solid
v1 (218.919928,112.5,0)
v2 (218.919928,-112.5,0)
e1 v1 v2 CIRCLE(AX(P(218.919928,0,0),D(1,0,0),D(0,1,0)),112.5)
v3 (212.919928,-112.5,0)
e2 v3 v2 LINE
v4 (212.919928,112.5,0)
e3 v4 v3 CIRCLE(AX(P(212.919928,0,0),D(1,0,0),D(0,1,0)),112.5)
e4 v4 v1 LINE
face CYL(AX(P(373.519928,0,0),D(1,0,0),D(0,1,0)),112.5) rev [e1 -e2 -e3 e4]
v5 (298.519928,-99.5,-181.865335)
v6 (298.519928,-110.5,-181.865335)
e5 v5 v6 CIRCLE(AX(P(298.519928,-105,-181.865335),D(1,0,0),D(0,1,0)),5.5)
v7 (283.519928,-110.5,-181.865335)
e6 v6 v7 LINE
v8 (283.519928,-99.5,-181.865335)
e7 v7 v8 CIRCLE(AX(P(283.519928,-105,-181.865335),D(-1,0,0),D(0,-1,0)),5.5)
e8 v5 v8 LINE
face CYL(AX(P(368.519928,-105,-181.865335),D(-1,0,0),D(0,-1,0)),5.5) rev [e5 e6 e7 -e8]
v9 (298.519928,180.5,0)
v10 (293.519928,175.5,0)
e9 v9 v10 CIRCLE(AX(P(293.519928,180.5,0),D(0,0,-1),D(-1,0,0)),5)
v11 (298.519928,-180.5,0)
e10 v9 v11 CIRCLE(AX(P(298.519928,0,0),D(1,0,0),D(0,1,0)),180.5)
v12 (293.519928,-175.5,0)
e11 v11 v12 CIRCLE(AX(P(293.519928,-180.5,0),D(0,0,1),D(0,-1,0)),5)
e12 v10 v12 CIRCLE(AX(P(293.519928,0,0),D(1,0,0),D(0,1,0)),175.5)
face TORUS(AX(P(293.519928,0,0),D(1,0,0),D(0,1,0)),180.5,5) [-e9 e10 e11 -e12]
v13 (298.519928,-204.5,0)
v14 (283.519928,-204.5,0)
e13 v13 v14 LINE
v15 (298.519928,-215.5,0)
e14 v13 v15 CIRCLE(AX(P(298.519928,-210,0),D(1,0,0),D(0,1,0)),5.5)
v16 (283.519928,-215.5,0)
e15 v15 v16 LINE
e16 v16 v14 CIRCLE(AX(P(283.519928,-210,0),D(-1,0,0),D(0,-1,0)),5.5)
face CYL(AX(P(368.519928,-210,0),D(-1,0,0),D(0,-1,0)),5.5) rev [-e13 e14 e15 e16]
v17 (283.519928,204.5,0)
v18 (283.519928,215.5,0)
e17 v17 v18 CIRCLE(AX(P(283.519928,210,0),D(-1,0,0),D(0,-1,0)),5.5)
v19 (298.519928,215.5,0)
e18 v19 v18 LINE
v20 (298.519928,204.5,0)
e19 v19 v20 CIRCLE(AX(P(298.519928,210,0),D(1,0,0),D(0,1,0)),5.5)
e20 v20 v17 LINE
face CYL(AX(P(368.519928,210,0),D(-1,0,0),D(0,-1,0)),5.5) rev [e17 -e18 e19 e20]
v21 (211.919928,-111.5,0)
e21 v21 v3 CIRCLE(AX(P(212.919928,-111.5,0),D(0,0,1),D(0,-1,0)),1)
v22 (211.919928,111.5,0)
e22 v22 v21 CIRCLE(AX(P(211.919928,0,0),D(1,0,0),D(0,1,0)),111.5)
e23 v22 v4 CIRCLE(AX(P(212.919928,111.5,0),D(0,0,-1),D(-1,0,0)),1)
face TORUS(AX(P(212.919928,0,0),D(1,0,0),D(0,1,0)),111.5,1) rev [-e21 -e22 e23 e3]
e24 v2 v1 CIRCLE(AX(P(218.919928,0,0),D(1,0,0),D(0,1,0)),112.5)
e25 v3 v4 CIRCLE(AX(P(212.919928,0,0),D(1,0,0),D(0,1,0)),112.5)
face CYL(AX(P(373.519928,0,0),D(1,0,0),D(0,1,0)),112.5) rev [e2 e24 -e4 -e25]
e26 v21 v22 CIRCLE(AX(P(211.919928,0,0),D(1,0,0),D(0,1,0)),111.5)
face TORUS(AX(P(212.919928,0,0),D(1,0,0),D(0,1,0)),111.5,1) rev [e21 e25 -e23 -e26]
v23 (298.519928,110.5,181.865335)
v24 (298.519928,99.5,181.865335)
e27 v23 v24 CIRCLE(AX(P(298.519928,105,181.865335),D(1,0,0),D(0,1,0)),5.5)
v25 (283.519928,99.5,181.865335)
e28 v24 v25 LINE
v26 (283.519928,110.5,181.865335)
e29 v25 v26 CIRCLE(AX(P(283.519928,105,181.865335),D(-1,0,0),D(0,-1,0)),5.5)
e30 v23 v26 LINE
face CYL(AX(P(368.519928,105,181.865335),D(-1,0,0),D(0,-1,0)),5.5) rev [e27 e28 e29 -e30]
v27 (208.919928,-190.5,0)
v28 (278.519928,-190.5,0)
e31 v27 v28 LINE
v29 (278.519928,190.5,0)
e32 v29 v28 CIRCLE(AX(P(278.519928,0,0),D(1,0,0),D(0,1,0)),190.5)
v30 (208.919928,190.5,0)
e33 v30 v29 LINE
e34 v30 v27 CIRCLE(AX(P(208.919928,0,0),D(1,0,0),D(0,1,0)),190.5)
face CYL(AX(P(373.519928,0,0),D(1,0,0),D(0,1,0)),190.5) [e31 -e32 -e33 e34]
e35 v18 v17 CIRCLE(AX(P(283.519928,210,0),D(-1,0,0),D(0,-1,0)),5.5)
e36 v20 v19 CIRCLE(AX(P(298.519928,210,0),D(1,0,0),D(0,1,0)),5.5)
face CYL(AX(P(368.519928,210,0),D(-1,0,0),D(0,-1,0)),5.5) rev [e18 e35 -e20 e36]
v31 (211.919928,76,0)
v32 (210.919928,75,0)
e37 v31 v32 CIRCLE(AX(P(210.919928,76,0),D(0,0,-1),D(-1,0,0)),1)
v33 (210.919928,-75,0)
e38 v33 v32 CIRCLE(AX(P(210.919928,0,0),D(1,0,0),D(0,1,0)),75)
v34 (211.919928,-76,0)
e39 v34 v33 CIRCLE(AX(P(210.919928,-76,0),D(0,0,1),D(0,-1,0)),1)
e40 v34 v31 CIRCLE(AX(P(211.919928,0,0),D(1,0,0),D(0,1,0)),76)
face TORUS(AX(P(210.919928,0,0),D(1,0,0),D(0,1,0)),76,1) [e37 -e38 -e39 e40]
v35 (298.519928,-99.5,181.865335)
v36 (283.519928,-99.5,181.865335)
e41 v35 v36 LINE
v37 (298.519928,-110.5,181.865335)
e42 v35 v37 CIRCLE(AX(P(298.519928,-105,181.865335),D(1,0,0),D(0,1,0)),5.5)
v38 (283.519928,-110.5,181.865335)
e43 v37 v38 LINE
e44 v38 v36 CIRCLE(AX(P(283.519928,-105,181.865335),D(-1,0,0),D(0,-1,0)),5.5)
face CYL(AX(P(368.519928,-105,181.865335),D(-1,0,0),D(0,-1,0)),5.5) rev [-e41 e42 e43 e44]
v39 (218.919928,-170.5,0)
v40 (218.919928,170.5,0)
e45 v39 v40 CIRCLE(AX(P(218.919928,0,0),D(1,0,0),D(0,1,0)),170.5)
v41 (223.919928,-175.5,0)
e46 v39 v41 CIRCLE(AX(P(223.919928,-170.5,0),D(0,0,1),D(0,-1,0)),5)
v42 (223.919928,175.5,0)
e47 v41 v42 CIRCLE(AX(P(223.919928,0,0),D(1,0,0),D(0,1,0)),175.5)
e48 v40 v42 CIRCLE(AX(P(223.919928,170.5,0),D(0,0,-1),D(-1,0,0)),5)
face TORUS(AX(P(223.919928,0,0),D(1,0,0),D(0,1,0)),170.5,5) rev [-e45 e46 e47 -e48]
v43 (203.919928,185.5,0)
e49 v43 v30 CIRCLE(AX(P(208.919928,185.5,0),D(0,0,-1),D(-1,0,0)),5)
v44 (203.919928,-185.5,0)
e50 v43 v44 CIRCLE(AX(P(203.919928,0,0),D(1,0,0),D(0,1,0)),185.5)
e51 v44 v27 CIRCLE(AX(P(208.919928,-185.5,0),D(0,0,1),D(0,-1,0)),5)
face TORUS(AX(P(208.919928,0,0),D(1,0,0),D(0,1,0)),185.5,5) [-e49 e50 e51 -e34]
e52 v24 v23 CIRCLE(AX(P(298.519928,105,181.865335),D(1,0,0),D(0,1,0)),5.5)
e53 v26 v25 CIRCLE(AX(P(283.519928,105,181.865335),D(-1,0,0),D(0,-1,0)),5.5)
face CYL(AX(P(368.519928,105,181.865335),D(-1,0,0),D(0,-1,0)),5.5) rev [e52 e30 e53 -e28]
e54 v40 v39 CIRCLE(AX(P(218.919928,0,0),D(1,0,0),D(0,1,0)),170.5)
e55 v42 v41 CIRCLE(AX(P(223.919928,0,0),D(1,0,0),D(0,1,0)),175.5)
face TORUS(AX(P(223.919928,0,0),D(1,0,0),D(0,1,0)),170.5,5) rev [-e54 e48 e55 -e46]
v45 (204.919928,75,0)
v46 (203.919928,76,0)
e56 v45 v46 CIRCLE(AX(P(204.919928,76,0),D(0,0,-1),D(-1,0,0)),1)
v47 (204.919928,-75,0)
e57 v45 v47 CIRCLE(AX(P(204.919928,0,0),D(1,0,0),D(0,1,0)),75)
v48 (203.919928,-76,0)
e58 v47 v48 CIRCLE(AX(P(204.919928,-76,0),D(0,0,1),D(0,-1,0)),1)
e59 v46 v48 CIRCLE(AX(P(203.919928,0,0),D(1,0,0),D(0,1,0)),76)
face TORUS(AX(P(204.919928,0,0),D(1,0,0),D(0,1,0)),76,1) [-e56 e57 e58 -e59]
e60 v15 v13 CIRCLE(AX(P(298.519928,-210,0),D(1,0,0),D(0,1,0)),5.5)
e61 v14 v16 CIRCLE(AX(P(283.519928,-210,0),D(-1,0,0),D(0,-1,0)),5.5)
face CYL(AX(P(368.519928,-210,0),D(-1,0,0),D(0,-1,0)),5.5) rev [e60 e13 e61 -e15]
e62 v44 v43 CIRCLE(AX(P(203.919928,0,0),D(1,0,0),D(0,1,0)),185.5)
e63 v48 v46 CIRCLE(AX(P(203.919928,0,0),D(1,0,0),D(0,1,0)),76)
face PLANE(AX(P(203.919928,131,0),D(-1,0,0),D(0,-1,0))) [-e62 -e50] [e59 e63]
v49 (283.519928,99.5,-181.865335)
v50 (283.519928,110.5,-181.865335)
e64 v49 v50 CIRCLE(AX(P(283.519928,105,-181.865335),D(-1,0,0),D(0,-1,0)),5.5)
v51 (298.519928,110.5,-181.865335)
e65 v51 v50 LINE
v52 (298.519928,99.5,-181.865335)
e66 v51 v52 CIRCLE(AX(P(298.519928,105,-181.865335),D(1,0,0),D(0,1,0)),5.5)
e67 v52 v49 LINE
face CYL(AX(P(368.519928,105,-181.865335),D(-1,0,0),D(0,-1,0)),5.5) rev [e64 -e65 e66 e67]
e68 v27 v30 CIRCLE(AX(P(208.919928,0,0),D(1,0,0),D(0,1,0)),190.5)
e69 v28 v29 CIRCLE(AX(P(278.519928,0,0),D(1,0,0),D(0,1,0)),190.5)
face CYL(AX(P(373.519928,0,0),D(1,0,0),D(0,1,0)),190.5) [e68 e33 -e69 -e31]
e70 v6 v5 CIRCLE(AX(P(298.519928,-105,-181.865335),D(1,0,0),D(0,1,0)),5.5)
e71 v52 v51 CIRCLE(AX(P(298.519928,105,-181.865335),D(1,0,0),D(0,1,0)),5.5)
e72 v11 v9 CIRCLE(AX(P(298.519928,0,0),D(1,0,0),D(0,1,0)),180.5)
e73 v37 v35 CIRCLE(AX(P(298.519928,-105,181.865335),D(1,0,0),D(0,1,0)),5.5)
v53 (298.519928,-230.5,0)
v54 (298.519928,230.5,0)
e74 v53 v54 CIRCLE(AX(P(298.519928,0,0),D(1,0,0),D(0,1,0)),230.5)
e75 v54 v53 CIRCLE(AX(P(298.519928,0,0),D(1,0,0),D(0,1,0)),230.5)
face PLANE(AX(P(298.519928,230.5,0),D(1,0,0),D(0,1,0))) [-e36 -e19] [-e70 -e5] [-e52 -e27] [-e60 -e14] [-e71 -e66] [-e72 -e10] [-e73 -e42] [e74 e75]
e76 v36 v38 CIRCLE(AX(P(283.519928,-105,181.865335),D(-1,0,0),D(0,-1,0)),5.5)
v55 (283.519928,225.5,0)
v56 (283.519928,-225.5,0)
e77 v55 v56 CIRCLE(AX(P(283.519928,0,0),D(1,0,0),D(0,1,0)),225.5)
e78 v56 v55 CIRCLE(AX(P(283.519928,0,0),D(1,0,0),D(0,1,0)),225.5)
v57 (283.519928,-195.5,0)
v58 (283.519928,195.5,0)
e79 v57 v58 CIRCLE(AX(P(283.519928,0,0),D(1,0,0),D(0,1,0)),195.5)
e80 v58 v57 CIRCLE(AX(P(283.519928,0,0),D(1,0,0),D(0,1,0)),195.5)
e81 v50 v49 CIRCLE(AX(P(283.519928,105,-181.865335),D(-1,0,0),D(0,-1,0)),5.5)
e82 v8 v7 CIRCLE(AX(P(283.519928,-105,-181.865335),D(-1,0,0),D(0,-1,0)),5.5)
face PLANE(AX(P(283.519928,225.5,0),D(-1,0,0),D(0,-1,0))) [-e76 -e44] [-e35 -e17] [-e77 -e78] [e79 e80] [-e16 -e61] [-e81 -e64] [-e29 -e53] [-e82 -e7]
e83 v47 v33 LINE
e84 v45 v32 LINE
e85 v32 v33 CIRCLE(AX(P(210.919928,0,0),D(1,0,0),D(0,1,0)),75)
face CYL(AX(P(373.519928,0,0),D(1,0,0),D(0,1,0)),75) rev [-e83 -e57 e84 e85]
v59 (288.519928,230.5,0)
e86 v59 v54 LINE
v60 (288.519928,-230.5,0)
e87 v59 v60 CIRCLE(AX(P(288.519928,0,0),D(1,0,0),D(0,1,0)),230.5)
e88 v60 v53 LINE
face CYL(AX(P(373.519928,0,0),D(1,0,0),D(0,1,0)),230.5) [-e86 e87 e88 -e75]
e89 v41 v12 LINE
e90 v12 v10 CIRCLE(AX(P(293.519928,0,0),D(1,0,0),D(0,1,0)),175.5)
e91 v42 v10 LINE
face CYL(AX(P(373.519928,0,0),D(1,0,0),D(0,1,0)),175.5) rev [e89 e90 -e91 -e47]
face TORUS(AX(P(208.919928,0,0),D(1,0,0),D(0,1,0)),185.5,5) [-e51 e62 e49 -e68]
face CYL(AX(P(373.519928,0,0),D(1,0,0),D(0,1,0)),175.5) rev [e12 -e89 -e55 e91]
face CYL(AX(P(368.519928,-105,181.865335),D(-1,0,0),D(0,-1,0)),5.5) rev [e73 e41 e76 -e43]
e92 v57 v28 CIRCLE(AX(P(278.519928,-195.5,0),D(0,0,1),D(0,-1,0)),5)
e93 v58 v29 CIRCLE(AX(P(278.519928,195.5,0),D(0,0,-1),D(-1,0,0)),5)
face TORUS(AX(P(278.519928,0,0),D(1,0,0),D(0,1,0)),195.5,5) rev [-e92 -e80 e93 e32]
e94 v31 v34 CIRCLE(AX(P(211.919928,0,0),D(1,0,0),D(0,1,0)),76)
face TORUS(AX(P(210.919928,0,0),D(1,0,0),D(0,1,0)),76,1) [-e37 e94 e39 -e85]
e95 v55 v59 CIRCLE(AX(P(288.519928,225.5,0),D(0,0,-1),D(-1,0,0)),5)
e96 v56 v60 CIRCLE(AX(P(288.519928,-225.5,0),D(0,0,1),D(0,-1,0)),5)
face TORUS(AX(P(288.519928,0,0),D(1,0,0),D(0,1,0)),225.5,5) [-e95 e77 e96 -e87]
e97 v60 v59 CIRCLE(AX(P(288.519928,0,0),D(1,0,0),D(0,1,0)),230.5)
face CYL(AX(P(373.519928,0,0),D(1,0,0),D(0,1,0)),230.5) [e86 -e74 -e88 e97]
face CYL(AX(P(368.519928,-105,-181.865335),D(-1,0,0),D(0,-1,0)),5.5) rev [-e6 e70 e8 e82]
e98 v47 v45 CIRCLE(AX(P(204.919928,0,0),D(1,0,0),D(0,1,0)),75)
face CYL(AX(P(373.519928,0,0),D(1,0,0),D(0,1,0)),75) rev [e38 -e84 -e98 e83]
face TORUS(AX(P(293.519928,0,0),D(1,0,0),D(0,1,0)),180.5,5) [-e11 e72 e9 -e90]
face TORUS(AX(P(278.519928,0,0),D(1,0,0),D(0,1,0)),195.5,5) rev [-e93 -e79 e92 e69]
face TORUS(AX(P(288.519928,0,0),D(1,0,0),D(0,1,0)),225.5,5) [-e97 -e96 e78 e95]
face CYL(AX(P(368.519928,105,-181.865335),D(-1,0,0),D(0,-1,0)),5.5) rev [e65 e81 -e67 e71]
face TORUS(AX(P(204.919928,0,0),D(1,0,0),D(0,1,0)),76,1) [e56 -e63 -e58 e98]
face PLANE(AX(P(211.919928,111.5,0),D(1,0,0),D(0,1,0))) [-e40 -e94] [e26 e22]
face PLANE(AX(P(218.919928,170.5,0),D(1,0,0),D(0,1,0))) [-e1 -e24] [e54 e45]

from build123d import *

# Parameters (mm, degrees)
SKETCH2_R          = 5.5
CUT_EXTRUDE1_DEPTH = 85


with BuildPart() as part:
    # Sketch1 → Revolve2 (revolve)
    with BuildSketch(Plane.XY):
        with BuildLine():
            Line((218.919928267, 112.5), (212.919928267, 112.5))
            ThreePointArc((212.919928267, 112.5), (212.212821486, 112.207106781), (211.919928267, 111.5))
            Line((211.919928267, 111.5), (211.919928267, 76))
            ThreePointArc((211.919928267, 76), (211.627035048, 75.292893219), (210.919928267, 75))
            Line((210.919928267, 75), (204.919928267, 75))
            ThreePointArc((204.919928267, 75), (204.212821486, 75.292893219), (203.919928267, 76))
            Line((203.919928267, 76), (203.919928267, 131))
            Line((203.919928267, 131), (203.919928267, 185.5))
            ThreePointArc((203.919928267, 185.5), (205.384394361, 189.035533906), (208.919928267, 190.5))
            Line((208.919928267, 190.5), (278.519928267, 190.5))
            ThreePointArc((278.519928267, 190.5), (282.055462173, 191.964466094), (283.519928267, 195.5))
            Line((283.519928267, 195.5), (283.519928267, 225.5))
            ThreePointArc((283.519928267, 225.5), (284.984394361, 229.035533906), (288.519928267, 230.5))
            Line((288.519928267, 230.5), (298.519928267, 230.5))
            Line((298.519928267, 230.5), (298.519928267, 205))
            Line((298.519928267, 205), (298.519928267, 180.5))
            ThreePointArc((298.519928267, 180.5), (297.055462173, 176.964466094), (293.519928267, 175.5))
            Line((293.519928267, 175.5), (223.919928267, 175.5))
            ThreePointArc((223.919928267, 175.5), (220.384394361, 174.035533906), (218.919928267, 170.5))
            Line((218.919928267, 170.5), (218.919928267, 131))
            Line((218.919928267, 131), (218.919928267, 112.5))
        make_face()
    revolve(axis=Axis((373.519928267, 0, 0), (-1, 0, 0)))

    # Sketch2 → Cut-Extrude1 (cut)
    with BuildSketch(Plane.ZY.offset(-283.519928267)):
        with Locations(Location((0, 210, 0), (0, 0, 270))):
            Circle(SKETCH2_R)
        with Locations(Location((181.865334795, 105, 0), (0, 0, 270))):
            Circle(SKETCH2_R)
        with Locations(Location((181.865334795, -105, 0), (0, 0, 270))):
            Circle(SKETCH2_R)
        with Locations(Location((0, -210, 0), (0, 0, 270))):
            Circle(SKETCH2_R)
        with Locations(Location((-181.865334795, -105, 0), (0, 0, 270))):
            Circle(SKETCH2_R)
        with Locations(Location((-181.865334795, 105, 0), (0, 0, 270))):
            Circle(SKETCH2_R)
    extrude(amount=-CUT_EXTRUDE1_DEPTH, mode=Mode.SUBTRACT)


solid = part.part
